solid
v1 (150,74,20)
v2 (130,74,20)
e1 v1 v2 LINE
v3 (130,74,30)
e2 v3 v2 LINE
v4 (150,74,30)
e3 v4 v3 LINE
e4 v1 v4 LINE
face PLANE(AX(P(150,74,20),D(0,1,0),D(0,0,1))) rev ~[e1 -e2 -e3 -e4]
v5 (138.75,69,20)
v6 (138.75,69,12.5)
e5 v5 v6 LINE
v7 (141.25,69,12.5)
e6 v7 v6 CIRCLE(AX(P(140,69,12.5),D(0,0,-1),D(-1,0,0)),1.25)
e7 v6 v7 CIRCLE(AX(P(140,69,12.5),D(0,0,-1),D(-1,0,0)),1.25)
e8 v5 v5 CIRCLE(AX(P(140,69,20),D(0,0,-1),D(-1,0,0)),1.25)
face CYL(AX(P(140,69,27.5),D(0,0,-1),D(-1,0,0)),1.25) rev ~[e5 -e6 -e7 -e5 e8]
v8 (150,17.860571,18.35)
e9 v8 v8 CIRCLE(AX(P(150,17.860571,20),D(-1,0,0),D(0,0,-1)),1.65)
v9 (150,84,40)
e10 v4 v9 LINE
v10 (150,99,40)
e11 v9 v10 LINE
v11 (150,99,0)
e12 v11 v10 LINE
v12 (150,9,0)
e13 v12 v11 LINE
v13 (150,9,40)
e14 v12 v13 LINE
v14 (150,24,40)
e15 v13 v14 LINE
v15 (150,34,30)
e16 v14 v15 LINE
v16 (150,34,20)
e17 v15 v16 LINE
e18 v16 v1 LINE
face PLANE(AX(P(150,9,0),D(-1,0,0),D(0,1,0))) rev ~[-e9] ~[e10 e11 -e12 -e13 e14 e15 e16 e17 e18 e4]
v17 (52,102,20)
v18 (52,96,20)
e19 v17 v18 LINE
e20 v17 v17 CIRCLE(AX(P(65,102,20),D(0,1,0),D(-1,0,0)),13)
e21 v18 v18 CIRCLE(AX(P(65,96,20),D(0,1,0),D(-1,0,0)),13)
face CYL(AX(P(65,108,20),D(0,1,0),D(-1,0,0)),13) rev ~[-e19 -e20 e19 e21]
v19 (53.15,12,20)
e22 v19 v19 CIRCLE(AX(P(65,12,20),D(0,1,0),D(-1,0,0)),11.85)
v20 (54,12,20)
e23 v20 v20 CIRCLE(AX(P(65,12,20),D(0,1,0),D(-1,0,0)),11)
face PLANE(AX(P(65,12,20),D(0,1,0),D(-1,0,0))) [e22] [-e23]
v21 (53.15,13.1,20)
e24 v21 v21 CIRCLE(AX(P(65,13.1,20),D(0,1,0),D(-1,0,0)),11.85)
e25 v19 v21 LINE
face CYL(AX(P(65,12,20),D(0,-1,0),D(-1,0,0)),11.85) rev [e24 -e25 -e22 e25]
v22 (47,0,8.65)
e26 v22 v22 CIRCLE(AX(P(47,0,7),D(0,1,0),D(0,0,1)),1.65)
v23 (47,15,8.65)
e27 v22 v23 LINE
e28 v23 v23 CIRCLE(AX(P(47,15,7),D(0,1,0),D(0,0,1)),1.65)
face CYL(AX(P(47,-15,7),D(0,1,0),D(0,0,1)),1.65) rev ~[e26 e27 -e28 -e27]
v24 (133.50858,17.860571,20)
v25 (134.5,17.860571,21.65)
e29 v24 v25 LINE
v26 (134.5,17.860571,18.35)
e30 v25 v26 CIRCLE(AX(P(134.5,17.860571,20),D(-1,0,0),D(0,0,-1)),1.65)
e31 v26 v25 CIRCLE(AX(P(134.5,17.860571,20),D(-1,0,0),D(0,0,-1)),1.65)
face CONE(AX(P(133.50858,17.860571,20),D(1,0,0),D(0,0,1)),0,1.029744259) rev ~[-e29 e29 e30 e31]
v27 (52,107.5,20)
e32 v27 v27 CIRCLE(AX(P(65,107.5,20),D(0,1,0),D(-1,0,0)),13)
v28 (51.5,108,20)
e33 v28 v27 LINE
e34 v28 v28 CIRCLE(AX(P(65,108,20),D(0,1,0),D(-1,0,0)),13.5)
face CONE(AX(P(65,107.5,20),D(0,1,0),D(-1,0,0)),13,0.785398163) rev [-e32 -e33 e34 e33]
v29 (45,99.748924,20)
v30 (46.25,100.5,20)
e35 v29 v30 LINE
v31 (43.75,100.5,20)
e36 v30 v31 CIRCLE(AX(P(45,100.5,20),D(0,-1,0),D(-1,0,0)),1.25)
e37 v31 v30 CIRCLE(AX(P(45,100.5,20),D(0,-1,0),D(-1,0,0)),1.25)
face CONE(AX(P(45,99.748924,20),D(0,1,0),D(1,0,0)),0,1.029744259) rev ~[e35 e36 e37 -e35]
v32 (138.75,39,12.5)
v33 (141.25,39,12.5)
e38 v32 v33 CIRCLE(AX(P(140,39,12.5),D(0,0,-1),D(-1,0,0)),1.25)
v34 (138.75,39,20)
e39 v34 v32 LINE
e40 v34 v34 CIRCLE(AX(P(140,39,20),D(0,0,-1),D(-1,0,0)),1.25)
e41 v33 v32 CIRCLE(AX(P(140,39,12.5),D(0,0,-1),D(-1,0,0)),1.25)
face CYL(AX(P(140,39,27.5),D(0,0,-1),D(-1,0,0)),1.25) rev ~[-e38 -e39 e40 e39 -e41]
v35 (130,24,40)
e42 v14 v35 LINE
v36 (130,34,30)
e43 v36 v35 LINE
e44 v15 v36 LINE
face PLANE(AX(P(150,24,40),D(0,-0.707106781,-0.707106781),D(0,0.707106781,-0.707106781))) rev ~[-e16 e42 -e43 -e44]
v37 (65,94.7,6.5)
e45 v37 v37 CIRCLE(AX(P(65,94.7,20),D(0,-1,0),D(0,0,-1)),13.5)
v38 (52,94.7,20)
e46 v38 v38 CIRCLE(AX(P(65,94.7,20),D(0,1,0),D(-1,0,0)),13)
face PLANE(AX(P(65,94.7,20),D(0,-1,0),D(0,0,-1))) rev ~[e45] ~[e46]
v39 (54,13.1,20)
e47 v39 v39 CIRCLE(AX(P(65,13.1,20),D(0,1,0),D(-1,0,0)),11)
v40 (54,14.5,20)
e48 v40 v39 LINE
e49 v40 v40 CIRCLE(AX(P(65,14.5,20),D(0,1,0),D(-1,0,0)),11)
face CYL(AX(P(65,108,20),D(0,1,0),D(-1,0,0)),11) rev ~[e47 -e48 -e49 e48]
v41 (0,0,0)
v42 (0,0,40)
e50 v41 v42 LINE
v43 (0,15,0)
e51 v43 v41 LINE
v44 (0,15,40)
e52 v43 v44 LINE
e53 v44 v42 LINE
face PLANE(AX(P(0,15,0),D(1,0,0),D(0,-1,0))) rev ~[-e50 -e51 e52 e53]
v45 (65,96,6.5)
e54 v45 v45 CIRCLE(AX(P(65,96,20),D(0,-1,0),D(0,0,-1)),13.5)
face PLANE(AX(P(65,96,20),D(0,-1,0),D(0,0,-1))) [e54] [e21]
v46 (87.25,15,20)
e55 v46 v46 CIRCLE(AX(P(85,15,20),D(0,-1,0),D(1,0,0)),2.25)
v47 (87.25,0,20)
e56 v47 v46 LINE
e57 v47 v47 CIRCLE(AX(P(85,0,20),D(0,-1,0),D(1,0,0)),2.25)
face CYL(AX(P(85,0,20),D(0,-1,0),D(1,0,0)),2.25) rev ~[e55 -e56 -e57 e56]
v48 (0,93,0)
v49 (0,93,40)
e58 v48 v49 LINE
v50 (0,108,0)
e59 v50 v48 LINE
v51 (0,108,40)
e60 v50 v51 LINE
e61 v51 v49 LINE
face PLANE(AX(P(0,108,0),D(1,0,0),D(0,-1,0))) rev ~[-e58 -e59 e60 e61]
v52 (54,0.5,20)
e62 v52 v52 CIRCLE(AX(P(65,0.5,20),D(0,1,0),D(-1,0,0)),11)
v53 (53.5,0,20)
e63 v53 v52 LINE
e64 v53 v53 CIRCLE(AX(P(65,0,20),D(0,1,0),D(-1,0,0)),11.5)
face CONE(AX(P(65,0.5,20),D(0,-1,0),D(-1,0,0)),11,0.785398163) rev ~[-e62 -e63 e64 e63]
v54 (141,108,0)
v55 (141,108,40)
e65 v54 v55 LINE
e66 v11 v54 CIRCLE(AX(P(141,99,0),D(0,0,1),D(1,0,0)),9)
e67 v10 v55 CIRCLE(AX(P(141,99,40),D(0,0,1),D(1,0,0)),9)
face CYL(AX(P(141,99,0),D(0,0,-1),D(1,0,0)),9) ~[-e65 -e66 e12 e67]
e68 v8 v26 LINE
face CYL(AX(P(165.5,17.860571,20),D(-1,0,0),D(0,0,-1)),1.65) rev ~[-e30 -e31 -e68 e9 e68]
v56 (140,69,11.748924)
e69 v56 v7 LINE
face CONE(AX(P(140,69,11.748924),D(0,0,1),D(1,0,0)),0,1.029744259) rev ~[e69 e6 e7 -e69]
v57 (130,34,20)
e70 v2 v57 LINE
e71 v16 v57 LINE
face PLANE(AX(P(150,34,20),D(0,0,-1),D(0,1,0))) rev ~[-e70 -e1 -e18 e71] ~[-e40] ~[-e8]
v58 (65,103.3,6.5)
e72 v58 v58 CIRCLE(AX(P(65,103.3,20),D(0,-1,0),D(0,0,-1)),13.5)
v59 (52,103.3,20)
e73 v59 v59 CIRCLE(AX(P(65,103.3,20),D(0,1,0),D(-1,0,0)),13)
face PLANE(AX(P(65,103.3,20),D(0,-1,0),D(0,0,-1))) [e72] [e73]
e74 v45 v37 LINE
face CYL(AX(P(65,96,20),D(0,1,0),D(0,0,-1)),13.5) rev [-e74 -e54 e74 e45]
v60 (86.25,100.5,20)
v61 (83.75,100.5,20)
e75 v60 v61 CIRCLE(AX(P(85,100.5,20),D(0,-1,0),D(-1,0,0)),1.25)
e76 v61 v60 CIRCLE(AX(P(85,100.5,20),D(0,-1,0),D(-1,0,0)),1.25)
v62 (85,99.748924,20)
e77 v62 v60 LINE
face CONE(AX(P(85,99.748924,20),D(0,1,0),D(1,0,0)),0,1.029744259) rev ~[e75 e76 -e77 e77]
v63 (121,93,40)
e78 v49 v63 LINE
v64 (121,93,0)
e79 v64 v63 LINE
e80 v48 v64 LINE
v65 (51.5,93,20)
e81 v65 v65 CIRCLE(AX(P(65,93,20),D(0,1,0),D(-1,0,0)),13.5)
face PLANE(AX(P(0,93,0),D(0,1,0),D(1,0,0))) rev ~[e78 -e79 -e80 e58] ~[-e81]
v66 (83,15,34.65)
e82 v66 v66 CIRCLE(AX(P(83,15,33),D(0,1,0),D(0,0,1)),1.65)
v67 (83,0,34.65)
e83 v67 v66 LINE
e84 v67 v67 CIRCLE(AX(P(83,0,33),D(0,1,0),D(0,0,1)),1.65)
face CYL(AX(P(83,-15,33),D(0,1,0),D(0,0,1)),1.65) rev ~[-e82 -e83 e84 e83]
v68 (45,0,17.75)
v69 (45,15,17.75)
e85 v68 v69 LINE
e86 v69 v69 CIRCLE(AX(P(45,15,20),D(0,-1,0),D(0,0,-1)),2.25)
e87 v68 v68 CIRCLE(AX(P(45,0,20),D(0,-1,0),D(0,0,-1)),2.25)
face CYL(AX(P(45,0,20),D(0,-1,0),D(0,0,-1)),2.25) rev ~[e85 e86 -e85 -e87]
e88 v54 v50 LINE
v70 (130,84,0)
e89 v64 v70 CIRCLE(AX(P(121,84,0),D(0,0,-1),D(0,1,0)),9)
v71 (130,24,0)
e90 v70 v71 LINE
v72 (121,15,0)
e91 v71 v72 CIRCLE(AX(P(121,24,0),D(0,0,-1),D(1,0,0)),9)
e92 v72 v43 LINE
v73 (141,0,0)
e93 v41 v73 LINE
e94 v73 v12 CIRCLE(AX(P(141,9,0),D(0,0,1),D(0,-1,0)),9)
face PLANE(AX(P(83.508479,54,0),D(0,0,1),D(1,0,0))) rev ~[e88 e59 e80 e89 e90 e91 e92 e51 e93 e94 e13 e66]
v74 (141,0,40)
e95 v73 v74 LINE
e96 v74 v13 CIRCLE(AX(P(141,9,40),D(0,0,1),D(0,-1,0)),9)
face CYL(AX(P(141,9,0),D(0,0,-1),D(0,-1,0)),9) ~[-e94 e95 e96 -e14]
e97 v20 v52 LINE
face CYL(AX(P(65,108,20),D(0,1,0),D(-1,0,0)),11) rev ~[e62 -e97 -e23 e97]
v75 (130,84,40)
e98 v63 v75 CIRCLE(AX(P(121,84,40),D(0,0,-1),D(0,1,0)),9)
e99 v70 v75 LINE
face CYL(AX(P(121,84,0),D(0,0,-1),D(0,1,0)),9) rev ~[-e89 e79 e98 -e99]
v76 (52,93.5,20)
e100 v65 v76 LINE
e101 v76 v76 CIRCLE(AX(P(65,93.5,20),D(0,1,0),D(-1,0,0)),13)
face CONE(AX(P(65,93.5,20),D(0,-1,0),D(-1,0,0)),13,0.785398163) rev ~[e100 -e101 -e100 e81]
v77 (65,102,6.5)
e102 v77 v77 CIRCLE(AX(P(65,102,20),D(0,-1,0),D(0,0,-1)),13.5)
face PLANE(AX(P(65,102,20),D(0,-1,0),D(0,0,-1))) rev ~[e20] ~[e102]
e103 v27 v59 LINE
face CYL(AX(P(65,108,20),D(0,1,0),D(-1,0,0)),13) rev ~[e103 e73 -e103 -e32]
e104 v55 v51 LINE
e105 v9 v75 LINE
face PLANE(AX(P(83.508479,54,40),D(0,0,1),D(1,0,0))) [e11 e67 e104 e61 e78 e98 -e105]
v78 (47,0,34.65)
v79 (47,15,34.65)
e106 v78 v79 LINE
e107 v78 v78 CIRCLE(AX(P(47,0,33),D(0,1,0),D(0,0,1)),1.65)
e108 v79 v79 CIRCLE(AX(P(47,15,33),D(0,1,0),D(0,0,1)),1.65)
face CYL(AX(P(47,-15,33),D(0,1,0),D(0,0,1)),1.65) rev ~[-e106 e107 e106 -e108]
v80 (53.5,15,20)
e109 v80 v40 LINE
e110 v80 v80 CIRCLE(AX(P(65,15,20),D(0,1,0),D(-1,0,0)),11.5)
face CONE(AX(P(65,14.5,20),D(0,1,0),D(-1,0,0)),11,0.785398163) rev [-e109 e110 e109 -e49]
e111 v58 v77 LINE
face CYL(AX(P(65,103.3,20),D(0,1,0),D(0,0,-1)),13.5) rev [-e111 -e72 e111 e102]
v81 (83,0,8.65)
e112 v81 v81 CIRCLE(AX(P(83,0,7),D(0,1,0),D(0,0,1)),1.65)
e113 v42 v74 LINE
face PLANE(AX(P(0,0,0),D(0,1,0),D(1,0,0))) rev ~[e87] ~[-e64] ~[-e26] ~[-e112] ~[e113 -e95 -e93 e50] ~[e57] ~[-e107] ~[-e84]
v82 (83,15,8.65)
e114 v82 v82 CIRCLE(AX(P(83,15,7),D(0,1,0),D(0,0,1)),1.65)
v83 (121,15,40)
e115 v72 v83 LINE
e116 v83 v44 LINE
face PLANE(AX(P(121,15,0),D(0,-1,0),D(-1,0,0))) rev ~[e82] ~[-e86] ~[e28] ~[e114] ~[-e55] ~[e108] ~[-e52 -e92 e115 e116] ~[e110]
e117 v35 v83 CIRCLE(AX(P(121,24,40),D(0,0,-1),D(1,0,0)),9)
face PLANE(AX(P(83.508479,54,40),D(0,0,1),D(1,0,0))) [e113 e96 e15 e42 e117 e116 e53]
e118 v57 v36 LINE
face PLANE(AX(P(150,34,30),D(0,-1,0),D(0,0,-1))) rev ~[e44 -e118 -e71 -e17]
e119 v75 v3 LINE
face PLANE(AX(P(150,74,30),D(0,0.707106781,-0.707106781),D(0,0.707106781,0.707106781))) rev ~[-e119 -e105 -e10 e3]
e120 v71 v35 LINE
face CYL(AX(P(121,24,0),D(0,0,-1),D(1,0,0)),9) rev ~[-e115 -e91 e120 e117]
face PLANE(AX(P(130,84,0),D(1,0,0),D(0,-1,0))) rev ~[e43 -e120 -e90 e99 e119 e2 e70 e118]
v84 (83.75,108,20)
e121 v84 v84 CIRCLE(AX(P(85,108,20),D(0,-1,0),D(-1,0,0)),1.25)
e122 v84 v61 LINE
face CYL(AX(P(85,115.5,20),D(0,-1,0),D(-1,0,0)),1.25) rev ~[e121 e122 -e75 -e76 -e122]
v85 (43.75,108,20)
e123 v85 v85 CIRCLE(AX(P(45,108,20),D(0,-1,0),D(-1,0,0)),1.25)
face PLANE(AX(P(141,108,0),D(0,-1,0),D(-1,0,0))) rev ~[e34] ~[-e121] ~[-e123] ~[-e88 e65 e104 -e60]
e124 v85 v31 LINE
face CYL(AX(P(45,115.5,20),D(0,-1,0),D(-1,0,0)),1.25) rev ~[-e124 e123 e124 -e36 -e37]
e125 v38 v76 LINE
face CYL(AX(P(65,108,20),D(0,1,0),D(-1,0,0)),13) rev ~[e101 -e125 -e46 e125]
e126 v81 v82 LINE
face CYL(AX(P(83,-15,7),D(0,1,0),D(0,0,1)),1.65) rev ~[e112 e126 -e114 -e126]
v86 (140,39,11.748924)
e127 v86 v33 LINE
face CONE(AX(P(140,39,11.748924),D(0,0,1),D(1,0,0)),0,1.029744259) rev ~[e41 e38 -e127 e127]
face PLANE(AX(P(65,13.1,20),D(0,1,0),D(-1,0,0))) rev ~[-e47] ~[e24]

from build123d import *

# Parameters (mm, degrees)
BOSS_EXTRUDE1_DEPTH   = 40
SKETCH2_R             = 11
CUT_EXTRUDE1_DEPTH    = 190.1137224
SKETCH3_R             = 13
CUT_EXTRUDE2_DEPTH    = 40
SKETCH4_R             = 11.85
CUT_EXTRUDE3_DEPTH    = 1.1
SKETCH5_R             = 13.5
CUT_EXTRUDE4_DEPTH    = 1.3
LPATTERN1_COUNT       = 2
LPATTERN1_PITCH       = 7.3
M3_TAPPED_HOLE1_D     = 2.5
M3_TAPPED_HOLE1_DEPTH = 7.5
M3_TAPPED_HOLE1_TIP   = 0.751075774
CUT_EXTRUDE5_REACH    = 191.114
CHAMFER1_SIZE         = 0.5
M3_TAPPED_HOLE2_D     = 2.5
M3_TAPPED_HOLE2_DEPTH = 7.5
M3_TAPPED_HOLE2_TIP   = 0.751075774
M4_TAPPED_HOLE1_D     = 3.3
M4_TAPPED_HOLE1_DEPTH = 15.5
M4_TAPPED_HOLE1_TIP   = 0.991420021
SKETCH14_R            = 2.25
CUT_EXTRUDE6_DEPTH    = 24
M4_TAPPED_HOLE2_D     = 3.3
M4_TAPPED_HOLE2_DEPTH = 15


with BuildPart() as part:
    # Sketch1 → Boss-Extrude1 (new body)
    with BuildSketch(Plane.XY):
        with BuildLine():
            Line((0, 0), (141, 0))
            ThreePointArc((141, 0), (147.363961031, 2.636038969), (150, 9))
            Line((150, 9), (150, 99))
            ThreePointArc((150, 99), (147.363961031, 105.363961031), (141, 108))
            Line((141, 108), (0, 108))
            Line((0, 108), (0, 93))
            Line((0, 93), (121, 93))
            ThreePointArc((121, 93), (127.363961031, 90.363961031), (130, 84))
            Line((130, 84), (130, 24))
            ThreePointArc((130, 24), (127.363961031, 17.636038969), (121, 15))
            Line((121, 15), (0, 15))
            Line((0, 15), (0, 0))
        make_face()
    extrude(amount=BOSS_EXTRUDE1_DEPTH)

    # Sketch2 → Cut-Extrude1 (cut, through all)
    with BuildSketch(Plane(origin=(0, 108, 0), x_dir=(1, 0, 0), z_dir=(0, 1, 0))):
        with Locations(Location((65, -20, 0), (0, 0, 180))):
            Circle(SKETCH2_R)
    extrude(amount=-CUT_EXTRUDE1_DEPTH, mode=Mode.SUBTRACT)

    # Sketch3 → Cut-Extrude2 (cut)
    with BuildSketch(Plane(origin=(0, 108, 0), x_dir=(1, 0, 0), z_dir=(0, 1, 0))):
        with Locations(Location((65, -20, 0), (0, 0, 180))):
            Circle(SKETCH3_R)
    extrude(amount=-CUT_EXTRUDE2_DEPTH, mode=Mode.SUBTRACT)

    # Sketch4 → Cut-Extrude3 (cut)
    with BuildSketch(Plane(origin=(0, 12, 0), x_dir=(1, 0, 0), z_dir=(0, 1, 0))):
        with Locations(Location((65, -20, 0), (0, 0, 180))):
            Circle(SKETCH4_R)
    extrude(amount=CUT_EXTRUDE3_DEPTH, mode=Mode.SUBTRACT)

    # Sketch5 → Cut-Extrude4 (cut)
    with BuildSketch(Plane(origin=(0, 96, 0), x_dir=(-1, 0, 0), z_dir=(0, -1, 0))):
        with Locations(Location((-65, -20, 0), (0, 0, 90))):
            Circle(SKETCH5_R)
    cut_extrude4 = extrude(amount=CUT_EXTRUDE4_DEPTH, mode=Mode.SUBTRACT)

    # LPattern1: Cut-Extrude4 ×2
    with Locations(*[(0, i * LPATTERN1_PITCH, 0) for i in range(1, LPATTERN1_COUNT)]):
        add(cut_extrude4, mode=Mode.SUBTRACT)

    # M3 Tapped Hole1
    with Locations(Plane(origin=(45, 108, 20), x_dir=(1, 0, 0), z_dir=(0, 1, 0))):
        with Locations((0, 0), (40, 0)):
            Hole(M3_TAPPED_HOLE1_D / 2, depth=M3_TAPPED_HOLE1_DEPTH)
            with Locations((0, 0, -(M3_TAPPED_HOLE1_DEPTH + M3_TAPPED_HOLE1_TIP / 2))):  # 118° drill point
                Cone(0, M3_TAPPED_HOLE1_D / 2, M3_TAPPED_HOLE1_TIP, mode=Mode.SUBTRACT)

    # Sketch9 → Cut-Extrude5 (cut, up to next)
    with BuildSketch(Plane(origin=(150, 0, 0), x_dir=(0, 0, -1), z_dir=(1, 0, 0)), mode=Mode.PRIVATE) as cut_extrude5_sk1:
        Polygon((-40, 24), (-30, 34), (-20, 34), (-20, 74), (-30, 74), (-40, 84), align=None)
    cut_extrude5_tool1 = extrude(cut_extrude5_sk1.sketch, amount=-CUT_EXTRUDE5_REACH, mode=Mode.PRIVATE) & part.part
    add(cut_extrude5_tool1.solids().sort_by_distance((150, 54, 30.740741))[0], mode=Mode.SUBTRACT)

    # Chamfer1
    chamfer1_edges = [part.edges().sort_by_distance(p)[0] for p in [
        (76, 0, 20),
        (76, 15, 20),
        (78, 93, 20),
        (78, 108, 20),
    ]]
    chamfer(chamfer1_edges, length=CHAMFER1_SIZE)

    # M3 Tapped Hole2
    with Locations(Plane(origin=(140, 69, 20), x_dir=(1, 0, 0), z_dir=(0, 0, 1))):
        with Locations((0, 0), (0, -30)):
            Hole(M3_TAPPED_HOLE2_D / 2, depth=M3_TAPPED_HOLE2_DEPTH)
            with Locations((0, 0, -(M3_TAPPED_HOLE2_DEPTH + M3_TAPPED_HOLE2_TIP / 2))):  # 118° drill point
                Cone(0, M3_TAPPED_HOLE2_D / 2, M3_TAPPED_HOLE2_TIP, mode=Mode.SUBTRACT)

    # M4 Tapped Hole1
    with Locations(Plane(origin=(150, 17.860571099, 20), x_dir=(0, 0, 1), z_dir=(1, 0, 0))):
        with Locations((0, 0)):
            Hole(M4_TAPPED_HOLE1_D / 2, depth=M4_TAPPED_HOLE1_DEPTH)
            with Locations((0, 0, -(M4_TAPPED_HOLE1_DEPTH + M4_TAPPED_HOLE1_TIP / 2))):  # 118° drill point
                Cone(0, M4_TAPPED_HOLE1_D / 2, M4_TAPPED_HOLE1_TIP, mode=Mode.SUBTRACT)

    # Sketch14 → Cut-Extrude6 (cut)
    with BuildSketch(Plane.XZ):
        with Locations((85, 20)):
            Circle(SKETCH14_R)
        with Locations(Location((45, 20, 0), (0, 0, 270))):
            Circle(SKETCH14_R)
    extrude(amount=-CUT_EXTRUDE6_DEPTH, mode=Mode.SUBTRACT)

    # M4 Tapped Hole2
    with Locations(Plane(origin=(47, 0, 33), x_dir=(0, 0, -1), z_dir=(0, -1, 0))):
        with Locations((0, 0), (0, 36), (26, 36), (26, 0)):
            Hole(M4_TAPPED_HOLE2_D / 2, depth=M4_TAPPED_HOLE2_DEPTH)


solid = part.part
